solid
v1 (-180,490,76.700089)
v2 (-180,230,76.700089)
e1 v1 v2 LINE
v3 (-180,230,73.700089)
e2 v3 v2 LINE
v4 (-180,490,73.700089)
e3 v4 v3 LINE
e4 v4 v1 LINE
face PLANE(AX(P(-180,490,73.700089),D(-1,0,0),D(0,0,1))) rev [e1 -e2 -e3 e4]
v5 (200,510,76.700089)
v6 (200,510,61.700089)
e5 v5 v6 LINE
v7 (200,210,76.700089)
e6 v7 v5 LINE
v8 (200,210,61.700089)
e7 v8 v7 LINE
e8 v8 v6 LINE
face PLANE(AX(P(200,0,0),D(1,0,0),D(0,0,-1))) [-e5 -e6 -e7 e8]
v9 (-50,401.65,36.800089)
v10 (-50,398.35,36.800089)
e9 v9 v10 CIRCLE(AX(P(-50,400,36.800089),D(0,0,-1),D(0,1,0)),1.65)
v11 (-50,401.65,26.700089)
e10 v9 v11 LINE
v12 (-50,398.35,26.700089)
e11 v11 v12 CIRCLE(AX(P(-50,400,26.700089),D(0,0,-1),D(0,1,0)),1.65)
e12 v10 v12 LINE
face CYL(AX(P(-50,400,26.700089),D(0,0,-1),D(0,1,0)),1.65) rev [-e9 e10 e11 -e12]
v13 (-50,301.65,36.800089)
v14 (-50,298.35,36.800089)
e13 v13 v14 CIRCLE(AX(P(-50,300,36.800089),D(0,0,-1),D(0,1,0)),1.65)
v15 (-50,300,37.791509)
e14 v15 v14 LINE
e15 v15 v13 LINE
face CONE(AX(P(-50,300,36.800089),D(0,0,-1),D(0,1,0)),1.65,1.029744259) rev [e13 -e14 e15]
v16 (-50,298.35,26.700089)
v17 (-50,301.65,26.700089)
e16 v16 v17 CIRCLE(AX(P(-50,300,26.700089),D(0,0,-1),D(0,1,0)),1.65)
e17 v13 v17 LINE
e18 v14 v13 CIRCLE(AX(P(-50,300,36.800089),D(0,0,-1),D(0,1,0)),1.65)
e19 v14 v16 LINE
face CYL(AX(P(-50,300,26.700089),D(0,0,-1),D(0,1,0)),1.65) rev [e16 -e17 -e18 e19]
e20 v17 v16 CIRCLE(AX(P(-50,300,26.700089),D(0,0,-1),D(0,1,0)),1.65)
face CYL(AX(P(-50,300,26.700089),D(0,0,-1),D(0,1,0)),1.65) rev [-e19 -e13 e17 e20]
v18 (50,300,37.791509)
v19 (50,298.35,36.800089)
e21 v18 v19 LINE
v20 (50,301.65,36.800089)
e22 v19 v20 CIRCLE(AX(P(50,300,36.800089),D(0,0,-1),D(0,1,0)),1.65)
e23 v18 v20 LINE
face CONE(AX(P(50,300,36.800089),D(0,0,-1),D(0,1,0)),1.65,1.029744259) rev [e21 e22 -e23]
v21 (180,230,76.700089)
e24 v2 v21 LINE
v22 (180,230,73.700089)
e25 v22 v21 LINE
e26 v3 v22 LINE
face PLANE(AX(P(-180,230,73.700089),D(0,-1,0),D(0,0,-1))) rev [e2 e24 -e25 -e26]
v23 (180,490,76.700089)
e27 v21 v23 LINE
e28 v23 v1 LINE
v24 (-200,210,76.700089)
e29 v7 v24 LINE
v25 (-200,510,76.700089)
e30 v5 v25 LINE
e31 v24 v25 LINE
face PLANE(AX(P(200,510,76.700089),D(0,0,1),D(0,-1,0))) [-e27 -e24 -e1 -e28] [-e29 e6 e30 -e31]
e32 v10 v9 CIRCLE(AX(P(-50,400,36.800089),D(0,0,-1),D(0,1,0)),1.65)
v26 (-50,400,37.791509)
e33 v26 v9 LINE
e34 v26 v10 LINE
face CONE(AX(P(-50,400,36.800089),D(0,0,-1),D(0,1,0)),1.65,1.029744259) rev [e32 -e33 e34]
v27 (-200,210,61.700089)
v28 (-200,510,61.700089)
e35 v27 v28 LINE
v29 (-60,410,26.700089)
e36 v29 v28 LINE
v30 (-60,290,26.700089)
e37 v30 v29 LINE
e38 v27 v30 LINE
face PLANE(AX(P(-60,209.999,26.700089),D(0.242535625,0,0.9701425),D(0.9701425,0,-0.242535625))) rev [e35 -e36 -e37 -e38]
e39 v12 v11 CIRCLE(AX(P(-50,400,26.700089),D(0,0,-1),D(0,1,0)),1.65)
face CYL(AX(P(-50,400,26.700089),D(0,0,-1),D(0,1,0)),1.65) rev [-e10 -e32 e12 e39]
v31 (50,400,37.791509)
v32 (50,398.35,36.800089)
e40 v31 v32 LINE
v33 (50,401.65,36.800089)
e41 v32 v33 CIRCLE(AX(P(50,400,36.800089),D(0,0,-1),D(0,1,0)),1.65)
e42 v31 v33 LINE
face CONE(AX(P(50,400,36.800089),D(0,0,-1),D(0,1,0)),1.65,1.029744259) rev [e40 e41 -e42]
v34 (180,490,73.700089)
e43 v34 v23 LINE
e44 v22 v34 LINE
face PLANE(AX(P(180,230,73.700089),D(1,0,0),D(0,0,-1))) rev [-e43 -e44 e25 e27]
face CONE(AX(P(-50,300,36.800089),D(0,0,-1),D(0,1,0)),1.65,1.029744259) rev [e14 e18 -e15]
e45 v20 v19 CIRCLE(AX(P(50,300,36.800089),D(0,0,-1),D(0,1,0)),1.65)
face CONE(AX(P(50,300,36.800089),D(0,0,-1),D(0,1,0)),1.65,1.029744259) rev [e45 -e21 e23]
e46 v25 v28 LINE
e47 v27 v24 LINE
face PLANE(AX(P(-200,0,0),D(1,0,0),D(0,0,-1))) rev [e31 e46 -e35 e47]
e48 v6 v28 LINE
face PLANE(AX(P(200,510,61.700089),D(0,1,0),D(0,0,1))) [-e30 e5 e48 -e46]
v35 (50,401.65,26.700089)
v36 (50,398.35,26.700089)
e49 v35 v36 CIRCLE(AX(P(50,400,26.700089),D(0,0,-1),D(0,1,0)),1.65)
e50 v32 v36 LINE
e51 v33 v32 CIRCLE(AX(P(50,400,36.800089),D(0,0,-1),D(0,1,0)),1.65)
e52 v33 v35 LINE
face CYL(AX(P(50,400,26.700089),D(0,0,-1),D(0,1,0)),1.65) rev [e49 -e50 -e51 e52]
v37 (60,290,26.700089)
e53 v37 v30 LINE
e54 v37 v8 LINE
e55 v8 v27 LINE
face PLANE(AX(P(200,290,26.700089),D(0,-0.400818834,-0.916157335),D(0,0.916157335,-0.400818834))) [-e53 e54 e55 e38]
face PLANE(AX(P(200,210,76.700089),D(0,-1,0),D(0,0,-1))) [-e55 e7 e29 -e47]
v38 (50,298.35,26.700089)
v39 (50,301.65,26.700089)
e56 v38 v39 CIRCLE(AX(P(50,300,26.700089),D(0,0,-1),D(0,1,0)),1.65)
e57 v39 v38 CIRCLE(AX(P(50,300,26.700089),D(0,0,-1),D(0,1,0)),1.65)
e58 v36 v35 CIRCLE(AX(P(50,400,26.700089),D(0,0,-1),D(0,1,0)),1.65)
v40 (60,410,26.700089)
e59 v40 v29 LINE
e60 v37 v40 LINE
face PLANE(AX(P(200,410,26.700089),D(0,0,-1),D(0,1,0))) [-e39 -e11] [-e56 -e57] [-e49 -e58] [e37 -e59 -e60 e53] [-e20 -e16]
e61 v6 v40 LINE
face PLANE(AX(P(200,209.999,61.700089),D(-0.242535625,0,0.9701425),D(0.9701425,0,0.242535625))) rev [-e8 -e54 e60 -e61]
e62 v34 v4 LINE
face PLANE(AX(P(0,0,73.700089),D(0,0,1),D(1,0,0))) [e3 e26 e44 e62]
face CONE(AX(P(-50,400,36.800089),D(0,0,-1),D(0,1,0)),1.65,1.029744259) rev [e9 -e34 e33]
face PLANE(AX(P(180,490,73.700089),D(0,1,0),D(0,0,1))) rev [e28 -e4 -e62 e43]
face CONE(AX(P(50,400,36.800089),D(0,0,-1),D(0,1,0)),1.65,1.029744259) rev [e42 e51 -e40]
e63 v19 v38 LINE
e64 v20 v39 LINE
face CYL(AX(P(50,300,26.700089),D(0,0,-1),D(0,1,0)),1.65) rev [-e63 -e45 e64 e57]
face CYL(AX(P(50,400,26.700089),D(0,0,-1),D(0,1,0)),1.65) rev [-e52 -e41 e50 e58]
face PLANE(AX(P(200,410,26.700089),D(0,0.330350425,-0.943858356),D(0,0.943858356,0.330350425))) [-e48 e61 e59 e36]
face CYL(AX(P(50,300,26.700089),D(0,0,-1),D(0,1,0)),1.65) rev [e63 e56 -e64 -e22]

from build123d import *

# Parameters (mm, degrees)
EXTRUDE_1_DEPTH        = 200
EXTRUDE_1_DEPTH_BACK   = 200
SKETCH_6_W             = 360
SKETCH_6_H             = 260
CUT_EXTRUDE_1_DEPTH    = 3
CUT_EXTRUDE_2_REACH    = 370.623
HOLE_WIZARD_M4_1_D     = 3.3
HOLE_WIZARD_M4_1_DEPTH = 10.1
HOLE_WIZARD_M4_1_TIP   = 0.991420021


with BuildPart() as part:
    # 草图5 → 凸台-拉伸1 (new, two sides: drawn at the far end of the back side and taken through both)
    with BuildSketch(Plane.ZY.offset(-EXTRUDE_1_DEPTH_BACK)):
        Polygon((26.700089157, 410), (61.700089157, 510), (76.700089157, 510), (76.700089157, 210), (61.700089157, 210), (26.700089157, 290), align=None)
    extrude(amount=EXTRUDE_1_DEPTH + EXTRUDE_1_DEPTH_BACK)

    # 草图6 → 切除-拉伸1 (cut)
    with BuildSketch(Plane.XY.offset(76.700089157)):
        with Locations((0, 360)):
            Rectangle(SKETCH_6_W, SKETCH_6_H)
    extrude(amount=-CUT_EXTRUDE_1_DEPTH, mode=Mode.SUBTRACT)

    # 草图8 → 切除-拉伸2 (cut, up to next)
    with BuildSketch(Plane(origin=(0, 510, 0), x_dir=(1, 0, 0), z_dir=(0, 1, 0)), mode=Mode.PRIVATE) as cut_extrude_2_sk1:
        Polygon((-200, -61.700089157), (-200, -26.700089157), (-60, -26.700089157), align=None)
    cut_extrude_2_tool1 = extrude(cut_extrude_2_sk1.sketch, amount=-CUT_EXTRUDE_2_REACH, mode=Mode.PRIVATE) & part.part
    # 草图8 → 切除-拉伸2 (cut, up to next)
    with BuildSketch(Plane(origin=(0, 510, 0), x_dir=(1, 0, 0), z_dir=(0, 1, 0)), mode=Mode.PRIVATE) as cut_extrude_2_sk2:
        Polygon((60, -26.700089157), (200, -26.700089157), (200, -61.700089157), align=None)
    cut_extrude_2_tool2 = extrude(cut_extrude_2_sk2.sketch, amount=-CUT_EXTRUDE_2_REACH, mode=Mode.PRIVATE) & part.part
    add(cut_extrude_2_tool1.solids().sort_by_distance((-153.333333, 510, 38.366756))[0], mode=Mode.SUBTRACT)
    add(cut_extrude_2_tool2.solids().sort_by_distance((153.333333, 510, 38.366756))[0], mode=Mode.SUBTRACT)

    # M4 螺纹孔1
    with Locations(Plane(origin=(0, 0, 26.700089157), x_dir=(-1, 0, 0), z_dir=(0, 0, -1))):
        with Locations((-50, 400), (50, 400), (50, 300), (-50, 300)):
            Hole(HOLE_WIZARD_M4_1_D / 2, depth=HOLE_WIZARD_M4_1_DEPTH)
            with Locations((0, 0, -(HOLE_WIZARD_M4_1_DEPTH + HOLE_WIZARD_M4_1_TIP / 2))):  # 118° drill point
                Cone(0, HOLE_WIZARD_M4_1_D / 2, HOLE_WIZARD_M4_1_TIP, mode=Mode.SUBTRACT)


solid = part.part
